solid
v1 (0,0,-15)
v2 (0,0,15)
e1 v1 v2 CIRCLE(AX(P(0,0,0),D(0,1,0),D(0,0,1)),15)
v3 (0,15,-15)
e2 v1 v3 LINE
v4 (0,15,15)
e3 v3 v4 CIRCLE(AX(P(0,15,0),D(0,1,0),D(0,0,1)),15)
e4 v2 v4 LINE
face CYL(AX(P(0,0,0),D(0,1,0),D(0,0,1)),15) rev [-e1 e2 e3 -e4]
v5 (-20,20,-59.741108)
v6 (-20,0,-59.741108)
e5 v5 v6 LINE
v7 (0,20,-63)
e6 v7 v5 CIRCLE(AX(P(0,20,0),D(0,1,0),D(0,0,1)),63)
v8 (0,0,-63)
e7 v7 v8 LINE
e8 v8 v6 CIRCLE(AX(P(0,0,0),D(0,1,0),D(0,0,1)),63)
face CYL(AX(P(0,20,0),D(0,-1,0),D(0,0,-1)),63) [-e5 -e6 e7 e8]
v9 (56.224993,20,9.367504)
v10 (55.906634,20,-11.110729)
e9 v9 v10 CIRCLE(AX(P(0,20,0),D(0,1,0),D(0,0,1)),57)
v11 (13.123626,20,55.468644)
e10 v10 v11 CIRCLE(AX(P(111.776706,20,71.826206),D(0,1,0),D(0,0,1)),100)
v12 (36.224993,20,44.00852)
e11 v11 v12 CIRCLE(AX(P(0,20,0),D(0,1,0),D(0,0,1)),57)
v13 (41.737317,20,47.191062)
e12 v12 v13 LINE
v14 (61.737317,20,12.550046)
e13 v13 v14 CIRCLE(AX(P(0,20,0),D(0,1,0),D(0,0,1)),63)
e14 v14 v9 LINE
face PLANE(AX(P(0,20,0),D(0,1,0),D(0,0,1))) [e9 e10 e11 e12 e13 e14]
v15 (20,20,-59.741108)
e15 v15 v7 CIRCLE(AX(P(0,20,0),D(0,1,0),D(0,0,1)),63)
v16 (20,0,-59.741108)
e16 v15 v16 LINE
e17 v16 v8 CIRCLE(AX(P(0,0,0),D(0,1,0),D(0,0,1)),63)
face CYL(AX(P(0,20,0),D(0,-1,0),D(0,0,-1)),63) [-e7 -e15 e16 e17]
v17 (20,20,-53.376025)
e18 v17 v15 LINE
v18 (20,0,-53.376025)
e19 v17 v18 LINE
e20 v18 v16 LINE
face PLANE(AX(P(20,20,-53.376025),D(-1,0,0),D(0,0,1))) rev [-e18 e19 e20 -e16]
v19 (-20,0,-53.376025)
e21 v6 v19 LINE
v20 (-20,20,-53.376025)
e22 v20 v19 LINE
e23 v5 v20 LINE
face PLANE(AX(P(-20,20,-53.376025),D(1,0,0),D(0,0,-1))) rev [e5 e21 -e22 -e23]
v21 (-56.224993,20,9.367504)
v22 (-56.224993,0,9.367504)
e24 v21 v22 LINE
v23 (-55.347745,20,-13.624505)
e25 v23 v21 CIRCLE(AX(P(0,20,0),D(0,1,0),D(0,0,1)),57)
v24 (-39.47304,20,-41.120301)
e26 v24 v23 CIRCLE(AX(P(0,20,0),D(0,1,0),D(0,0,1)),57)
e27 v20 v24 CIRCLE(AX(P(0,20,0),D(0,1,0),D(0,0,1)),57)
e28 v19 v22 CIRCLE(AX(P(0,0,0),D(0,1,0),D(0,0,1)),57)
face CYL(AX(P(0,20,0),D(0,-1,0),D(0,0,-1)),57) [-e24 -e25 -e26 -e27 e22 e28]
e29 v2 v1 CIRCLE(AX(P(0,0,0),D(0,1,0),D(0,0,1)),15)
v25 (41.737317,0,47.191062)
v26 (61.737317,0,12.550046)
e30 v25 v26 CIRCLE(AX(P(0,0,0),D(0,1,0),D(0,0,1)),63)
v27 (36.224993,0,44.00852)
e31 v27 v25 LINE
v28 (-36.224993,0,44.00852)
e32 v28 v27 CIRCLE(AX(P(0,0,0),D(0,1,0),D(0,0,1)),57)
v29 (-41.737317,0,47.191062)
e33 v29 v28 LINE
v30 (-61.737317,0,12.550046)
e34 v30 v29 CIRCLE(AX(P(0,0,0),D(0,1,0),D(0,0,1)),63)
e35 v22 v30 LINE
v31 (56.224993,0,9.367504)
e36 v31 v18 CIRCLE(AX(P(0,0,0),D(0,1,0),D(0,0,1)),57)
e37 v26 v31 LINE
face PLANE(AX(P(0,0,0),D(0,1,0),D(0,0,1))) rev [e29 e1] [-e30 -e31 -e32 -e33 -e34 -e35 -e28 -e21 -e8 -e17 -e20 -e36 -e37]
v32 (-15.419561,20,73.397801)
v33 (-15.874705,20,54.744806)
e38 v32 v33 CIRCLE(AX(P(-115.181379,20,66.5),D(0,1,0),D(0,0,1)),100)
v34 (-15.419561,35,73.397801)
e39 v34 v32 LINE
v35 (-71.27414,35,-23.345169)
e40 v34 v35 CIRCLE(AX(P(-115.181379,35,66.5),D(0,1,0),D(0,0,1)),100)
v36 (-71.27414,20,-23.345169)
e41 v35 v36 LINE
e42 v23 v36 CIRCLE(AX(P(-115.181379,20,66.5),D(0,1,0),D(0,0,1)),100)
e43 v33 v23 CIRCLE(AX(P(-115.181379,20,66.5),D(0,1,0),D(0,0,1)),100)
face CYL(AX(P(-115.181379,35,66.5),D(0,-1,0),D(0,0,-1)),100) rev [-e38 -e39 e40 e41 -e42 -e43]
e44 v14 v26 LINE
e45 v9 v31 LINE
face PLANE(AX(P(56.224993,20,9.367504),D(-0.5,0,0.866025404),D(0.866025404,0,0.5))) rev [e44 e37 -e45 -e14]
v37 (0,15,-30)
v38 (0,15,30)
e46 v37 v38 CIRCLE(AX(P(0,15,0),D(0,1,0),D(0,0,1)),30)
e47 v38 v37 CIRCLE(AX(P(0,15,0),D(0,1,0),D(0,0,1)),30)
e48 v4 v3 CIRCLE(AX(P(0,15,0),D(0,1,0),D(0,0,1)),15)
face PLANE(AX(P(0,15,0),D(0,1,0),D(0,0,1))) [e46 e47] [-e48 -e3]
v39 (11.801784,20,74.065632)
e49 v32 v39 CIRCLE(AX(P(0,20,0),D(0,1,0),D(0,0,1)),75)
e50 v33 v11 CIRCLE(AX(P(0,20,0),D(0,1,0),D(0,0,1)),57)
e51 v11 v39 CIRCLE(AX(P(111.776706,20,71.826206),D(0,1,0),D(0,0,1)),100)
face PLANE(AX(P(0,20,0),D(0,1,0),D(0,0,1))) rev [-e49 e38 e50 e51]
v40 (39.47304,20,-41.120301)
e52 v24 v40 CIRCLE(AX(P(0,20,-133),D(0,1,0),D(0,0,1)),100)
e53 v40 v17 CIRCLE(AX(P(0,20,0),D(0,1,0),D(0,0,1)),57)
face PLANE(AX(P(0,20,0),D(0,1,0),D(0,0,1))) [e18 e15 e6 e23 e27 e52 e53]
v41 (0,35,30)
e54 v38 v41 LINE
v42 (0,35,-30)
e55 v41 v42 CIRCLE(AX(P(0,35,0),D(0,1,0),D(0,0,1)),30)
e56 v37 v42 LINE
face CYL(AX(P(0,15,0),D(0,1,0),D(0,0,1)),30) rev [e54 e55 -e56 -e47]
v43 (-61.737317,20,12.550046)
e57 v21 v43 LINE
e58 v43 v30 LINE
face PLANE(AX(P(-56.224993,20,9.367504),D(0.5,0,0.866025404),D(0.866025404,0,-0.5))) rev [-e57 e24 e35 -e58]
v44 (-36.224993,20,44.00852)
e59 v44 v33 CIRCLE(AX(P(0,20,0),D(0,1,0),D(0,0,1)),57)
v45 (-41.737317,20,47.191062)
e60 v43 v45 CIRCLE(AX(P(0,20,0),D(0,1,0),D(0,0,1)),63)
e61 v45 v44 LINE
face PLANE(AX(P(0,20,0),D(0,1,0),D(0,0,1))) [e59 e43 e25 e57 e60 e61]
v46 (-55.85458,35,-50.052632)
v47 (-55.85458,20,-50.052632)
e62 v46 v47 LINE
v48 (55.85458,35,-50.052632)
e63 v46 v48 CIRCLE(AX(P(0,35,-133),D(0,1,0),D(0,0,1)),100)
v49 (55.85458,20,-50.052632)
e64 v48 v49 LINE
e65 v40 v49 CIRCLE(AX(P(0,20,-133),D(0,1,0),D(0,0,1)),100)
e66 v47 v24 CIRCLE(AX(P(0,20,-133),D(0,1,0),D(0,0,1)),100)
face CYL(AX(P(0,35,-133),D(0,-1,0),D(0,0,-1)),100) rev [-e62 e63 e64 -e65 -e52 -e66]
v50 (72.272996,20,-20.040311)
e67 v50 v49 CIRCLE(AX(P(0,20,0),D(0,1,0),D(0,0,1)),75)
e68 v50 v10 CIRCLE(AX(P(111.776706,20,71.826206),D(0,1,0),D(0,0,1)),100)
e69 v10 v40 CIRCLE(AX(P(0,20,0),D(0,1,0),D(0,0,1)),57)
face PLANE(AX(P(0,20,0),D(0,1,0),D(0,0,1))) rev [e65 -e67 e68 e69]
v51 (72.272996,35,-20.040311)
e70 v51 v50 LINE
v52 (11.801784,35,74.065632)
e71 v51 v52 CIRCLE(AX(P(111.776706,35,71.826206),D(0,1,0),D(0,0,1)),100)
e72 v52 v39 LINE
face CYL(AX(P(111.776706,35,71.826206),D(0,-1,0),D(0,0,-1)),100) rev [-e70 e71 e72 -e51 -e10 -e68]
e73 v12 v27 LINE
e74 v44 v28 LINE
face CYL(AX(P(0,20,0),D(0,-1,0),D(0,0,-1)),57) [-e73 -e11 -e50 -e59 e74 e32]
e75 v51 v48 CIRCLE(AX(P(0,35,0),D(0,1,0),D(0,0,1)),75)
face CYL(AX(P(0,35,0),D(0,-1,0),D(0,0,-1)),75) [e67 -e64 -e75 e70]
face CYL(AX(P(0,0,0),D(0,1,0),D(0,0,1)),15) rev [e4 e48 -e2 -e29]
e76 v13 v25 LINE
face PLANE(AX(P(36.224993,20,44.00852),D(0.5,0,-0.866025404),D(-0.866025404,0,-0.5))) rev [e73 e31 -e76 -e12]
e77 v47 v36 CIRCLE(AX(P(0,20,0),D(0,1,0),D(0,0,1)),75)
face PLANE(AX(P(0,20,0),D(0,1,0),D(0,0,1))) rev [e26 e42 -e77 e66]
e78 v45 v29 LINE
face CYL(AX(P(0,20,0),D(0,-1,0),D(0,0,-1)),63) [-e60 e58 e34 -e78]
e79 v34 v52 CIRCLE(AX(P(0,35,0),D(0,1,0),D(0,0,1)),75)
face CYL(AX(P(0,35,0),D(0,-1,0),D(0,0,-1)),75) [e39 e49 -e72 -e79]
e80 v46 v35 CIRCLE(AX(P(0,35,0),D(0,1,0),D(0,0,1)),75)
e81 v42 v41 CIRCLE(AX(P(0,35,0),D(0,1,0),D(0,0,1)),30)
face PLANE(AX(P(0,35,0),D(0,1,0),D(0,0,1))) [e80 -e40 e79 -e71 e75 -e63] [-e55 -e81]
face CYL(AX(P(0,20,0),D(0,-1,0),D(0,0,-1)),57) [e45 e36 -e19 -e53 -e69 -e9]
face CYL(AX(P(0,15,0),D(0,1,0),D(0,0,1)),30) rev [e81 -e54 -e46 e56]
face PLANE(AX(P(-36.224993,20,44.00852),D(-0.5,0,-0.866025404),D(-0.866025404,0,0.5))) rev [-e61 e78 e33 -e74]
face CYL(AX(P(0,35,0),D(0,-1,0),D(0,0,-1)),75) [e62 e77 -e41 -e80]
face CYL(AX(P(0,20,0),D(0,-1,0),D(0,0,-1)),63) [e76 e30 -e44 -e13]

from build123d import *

# Parameters (mm, degrees)
BASE_DISC_20MM_DEPTH        = 20
THREE_LOBE_BOSS_15MM_DEPTH  = 15
COUNTERBORE_PROFILE_R       = 30
COUNTERBORE_20MM_DEEP_DEPTH = 20
THROUGH_BORE_PROFILE_R      = 15
THROUGH_BORE_DEPTH          = 107.05840812


with BuildPart() as part:
    # Base Disc Profile → Base Disc 20mm (new body)
    with BuildSketch(Plane(origin=(0, 0, 0), x_dir=(1, 0, 0), z_dir=(0, 1, 0))):
        with BuildLine():
            Line((-20, 53.37602458), (-20, 59.741108125))
            ThreePointArc((-20, 59.741108125), (0, 63), (20, 59.741108125))
            Line((20, 59.741108125), (20, 53.37602458))
            ThreePointArc((20, 53.37602458), (49.363448016, 28.5), (56.22499324, -9.367504214))
            Line((56.22499324, -9.367504214), (61.737317286, -12.550045987))
            ThreePointArc((61.737317286, -12.550045987), (54.559600438, -31.5), (41.737317286, -47.191062138))
            Line((41.737317286, -47.191062138), (36.22499324, -44.008520366))
            ThreePointArc((36.22499324, -44.008520366), (0, -57), (-36.22499324, -44.008520366))
            Line((-36.22499324, -44.008520366), (-41.737317286, -47.191062138))
            ThreePointArc((-41.737317286, -47.191062138), (-54.559600438, -31.5), (-61.737317286, -12.550045987))
            Line((-61.737317286, -12.550045987), (-56.22499324, -9.367504214))
            ThreePointArc((-56.22499324, -9.367504214), (-49.363448016, 28.5), (-20, 53.37602458))
        make_face()
    extrude(amount=BASE_DISC_20MM_DEPTH)

    # Three-Lobe Profile → Three-Lobe Boss 15mm (add)
    with BuildSketch(Plane(origin=(0, 20, 0), x_dir=(1, 0, 0), z_dir=(0, 1, 0))):
        with BuildLine():
            ThreePointArc((39.473039737, 41.120300752), (0, 33), (-39.473039737, 41.120300752))
            ThreePointArc((-39.473039737, 41.120300752), (-49.363448016, 28.5), (-55.347744931, 13.624504801))
            ThreePointArc((-55.347744931, 13.624504801), (-28.578838325, -16.5), (-15.874705194, -54.744805553))
            ThreePointArc((-15.874705194, -54.744805553), (-1.422355425, -56.98225079), (13.123625771, -55.468643815))
            ThreePointArc((13.123625771, -55.468643815), (27.648504036, -17.766556361), (55.906633869, 11.110728574))
            ThreePointArc((55.906633869, 11.110728574), (49.994641111, 27.377652568), (39.473039737, 41.120300752))
        make_face()
        with BuildLine():
            ThreePointArc((-39.473039737, 41.120300752), (-44.717521746, 43.555362101), (-49.812494678, 46.289473684))
            ThreePointArc((-49.812494678, 46.289473684), (-58.889727457, 34), (-64.994107477, 19.994148975))
            ThreePointArc((-64.994107477, 19.994148975), (-60.078810924, 16.948828776), (-55.347744931, 13.624504801))
            ThreePointArc((-55.347744931, 13.624504801), (-49.363448016, 28.5), (-39.473039737, 41.120300752))
        make_face()
        with BuildLine():
            ThreePointArc((-49.812494678, 46.289473684), (-52.867031225, 48.117274965), (-55.854579687, 50.052631579))
            ThreePointArc((-55.854579687, 50.052631579), (-64.951905284, 37.5), (-71.274140317, 23.345169137))
            ThreePointArc((-71.274140317, 23.345169137), (-68.104298093, 21.725554581), (-64.994107477, 19.994148975))
            ThreePointArc((-64.994107477, 19.994148975), (-58.889727457, 34), (-49.812494678, 46.289473684))
        make_face()
        with BuildLine():
            ThreePointArc((13.123625771, -55.468643815), (-1.422355425, -56.98225079), (-15.874705194, -54.744805553))
            ThreePointArc((-15.874705194, -54.744805553), (-15.361289177, -60.504190877), (-15.181612799, -66.283622659))
            ThreePointArc((-15.181612799, -66.283622659), (-1.676596285, -67.979327923), (11.895593178, -66.951436601))
            ThreePointArc((11.895593178, -66.951436601), (12.343713059, -61.192298339), (13.123625771, -55.468643815))
        make_face()
        with BuildLine():
            ThreePointArc((11.895593178, -66.951436601), (-1.676596285, -67.979327923), (-15.181612799, -66.283622659))
            ThreePointArc((-15.181612799, -66.283622659), (-15.237266868, -69.842829546), (-15.41956063, -73.397800716))
            ThreePointArc((-15.41956063, -73.397800716), (-1.839450143, -74.977439428), (11.801783935, -74.065632354))
            ThreePointArc((11.801783935, -74.065632354), (11.7853983, -70.507699919), (11.895593178, -66.951436601))
        make_face()
        with BuildLine():
            ThreePointArc((49.812494678, 46.289473684), (44.717521746, 43.555362101), (39.473039737, 41.120300752))
            ThreePointArc((39.473039737, 41.120300752), (49.994641111, 27.377652568), (55.906633869, 11.110728574))
            ThreePointArc((55.906633869, 11.110728574), (60.78874038, 14.198368606), (65.840986006, 16.998957666))
            ThreePointArc((65.840986006, 16.998957666), (59.652455781, 32.643292102), (49.812494678, 46.289473684))
        make_face()
        with BuildLine():
            ThreePointArc((55.854579687, 50.052631579), (52.867031225, 48.117274965), (49.812494678, 46.289473684))
            ThreePointArc((49.812494678, 46.289473684), (59.652455781, 32.643292102), (65.840986006, 16.998957666))
            ThreePointArc((65.840986006, 16.998957666), (69.029934048, 18.576855661), (72.272995877, 20.04031105))
            ThreePointArc((72.272995877, 20.04031105), (65.797824819, 35.995086458), (55.854579687, 50.052631579))
        make_face()
    extrude(amount=THREE_LOBE_BOSS_15MM_DEPTH)

    # Counterbore Profile → Counterbore 20mm Deep (cut)
    with BuildSketch(Plane(origin=(0, 35, 0), x_dir=(1, 0, 0), z_dir=(0, 1, 0))):
        with Locations(Location((0, 0, 0), (0, 0, 270))):
            Circle(COUNTERBORE_PROFILE_R)
    extrude(amount=-COUNTERBORE_20MM_DEEP_DEPTH, mode=Mode.SUBTRACT)

    # Through Bore Profile → Through Bore (cut, through all)
    with BuildSketch(Plane(origin=(0, 15, 0), x_dir=(1, 0, 0), z_dir=(0, 1, 0))):
        with Locations(Location((0, 0, 0), (0, 0, 270))):
            Circle(THROUGH_BORE_PROFILE_R)
    extrude(amount=-THROUGH_BORE_DEPTH, mode=Mode.SUBTRACT)


solid = part.part
